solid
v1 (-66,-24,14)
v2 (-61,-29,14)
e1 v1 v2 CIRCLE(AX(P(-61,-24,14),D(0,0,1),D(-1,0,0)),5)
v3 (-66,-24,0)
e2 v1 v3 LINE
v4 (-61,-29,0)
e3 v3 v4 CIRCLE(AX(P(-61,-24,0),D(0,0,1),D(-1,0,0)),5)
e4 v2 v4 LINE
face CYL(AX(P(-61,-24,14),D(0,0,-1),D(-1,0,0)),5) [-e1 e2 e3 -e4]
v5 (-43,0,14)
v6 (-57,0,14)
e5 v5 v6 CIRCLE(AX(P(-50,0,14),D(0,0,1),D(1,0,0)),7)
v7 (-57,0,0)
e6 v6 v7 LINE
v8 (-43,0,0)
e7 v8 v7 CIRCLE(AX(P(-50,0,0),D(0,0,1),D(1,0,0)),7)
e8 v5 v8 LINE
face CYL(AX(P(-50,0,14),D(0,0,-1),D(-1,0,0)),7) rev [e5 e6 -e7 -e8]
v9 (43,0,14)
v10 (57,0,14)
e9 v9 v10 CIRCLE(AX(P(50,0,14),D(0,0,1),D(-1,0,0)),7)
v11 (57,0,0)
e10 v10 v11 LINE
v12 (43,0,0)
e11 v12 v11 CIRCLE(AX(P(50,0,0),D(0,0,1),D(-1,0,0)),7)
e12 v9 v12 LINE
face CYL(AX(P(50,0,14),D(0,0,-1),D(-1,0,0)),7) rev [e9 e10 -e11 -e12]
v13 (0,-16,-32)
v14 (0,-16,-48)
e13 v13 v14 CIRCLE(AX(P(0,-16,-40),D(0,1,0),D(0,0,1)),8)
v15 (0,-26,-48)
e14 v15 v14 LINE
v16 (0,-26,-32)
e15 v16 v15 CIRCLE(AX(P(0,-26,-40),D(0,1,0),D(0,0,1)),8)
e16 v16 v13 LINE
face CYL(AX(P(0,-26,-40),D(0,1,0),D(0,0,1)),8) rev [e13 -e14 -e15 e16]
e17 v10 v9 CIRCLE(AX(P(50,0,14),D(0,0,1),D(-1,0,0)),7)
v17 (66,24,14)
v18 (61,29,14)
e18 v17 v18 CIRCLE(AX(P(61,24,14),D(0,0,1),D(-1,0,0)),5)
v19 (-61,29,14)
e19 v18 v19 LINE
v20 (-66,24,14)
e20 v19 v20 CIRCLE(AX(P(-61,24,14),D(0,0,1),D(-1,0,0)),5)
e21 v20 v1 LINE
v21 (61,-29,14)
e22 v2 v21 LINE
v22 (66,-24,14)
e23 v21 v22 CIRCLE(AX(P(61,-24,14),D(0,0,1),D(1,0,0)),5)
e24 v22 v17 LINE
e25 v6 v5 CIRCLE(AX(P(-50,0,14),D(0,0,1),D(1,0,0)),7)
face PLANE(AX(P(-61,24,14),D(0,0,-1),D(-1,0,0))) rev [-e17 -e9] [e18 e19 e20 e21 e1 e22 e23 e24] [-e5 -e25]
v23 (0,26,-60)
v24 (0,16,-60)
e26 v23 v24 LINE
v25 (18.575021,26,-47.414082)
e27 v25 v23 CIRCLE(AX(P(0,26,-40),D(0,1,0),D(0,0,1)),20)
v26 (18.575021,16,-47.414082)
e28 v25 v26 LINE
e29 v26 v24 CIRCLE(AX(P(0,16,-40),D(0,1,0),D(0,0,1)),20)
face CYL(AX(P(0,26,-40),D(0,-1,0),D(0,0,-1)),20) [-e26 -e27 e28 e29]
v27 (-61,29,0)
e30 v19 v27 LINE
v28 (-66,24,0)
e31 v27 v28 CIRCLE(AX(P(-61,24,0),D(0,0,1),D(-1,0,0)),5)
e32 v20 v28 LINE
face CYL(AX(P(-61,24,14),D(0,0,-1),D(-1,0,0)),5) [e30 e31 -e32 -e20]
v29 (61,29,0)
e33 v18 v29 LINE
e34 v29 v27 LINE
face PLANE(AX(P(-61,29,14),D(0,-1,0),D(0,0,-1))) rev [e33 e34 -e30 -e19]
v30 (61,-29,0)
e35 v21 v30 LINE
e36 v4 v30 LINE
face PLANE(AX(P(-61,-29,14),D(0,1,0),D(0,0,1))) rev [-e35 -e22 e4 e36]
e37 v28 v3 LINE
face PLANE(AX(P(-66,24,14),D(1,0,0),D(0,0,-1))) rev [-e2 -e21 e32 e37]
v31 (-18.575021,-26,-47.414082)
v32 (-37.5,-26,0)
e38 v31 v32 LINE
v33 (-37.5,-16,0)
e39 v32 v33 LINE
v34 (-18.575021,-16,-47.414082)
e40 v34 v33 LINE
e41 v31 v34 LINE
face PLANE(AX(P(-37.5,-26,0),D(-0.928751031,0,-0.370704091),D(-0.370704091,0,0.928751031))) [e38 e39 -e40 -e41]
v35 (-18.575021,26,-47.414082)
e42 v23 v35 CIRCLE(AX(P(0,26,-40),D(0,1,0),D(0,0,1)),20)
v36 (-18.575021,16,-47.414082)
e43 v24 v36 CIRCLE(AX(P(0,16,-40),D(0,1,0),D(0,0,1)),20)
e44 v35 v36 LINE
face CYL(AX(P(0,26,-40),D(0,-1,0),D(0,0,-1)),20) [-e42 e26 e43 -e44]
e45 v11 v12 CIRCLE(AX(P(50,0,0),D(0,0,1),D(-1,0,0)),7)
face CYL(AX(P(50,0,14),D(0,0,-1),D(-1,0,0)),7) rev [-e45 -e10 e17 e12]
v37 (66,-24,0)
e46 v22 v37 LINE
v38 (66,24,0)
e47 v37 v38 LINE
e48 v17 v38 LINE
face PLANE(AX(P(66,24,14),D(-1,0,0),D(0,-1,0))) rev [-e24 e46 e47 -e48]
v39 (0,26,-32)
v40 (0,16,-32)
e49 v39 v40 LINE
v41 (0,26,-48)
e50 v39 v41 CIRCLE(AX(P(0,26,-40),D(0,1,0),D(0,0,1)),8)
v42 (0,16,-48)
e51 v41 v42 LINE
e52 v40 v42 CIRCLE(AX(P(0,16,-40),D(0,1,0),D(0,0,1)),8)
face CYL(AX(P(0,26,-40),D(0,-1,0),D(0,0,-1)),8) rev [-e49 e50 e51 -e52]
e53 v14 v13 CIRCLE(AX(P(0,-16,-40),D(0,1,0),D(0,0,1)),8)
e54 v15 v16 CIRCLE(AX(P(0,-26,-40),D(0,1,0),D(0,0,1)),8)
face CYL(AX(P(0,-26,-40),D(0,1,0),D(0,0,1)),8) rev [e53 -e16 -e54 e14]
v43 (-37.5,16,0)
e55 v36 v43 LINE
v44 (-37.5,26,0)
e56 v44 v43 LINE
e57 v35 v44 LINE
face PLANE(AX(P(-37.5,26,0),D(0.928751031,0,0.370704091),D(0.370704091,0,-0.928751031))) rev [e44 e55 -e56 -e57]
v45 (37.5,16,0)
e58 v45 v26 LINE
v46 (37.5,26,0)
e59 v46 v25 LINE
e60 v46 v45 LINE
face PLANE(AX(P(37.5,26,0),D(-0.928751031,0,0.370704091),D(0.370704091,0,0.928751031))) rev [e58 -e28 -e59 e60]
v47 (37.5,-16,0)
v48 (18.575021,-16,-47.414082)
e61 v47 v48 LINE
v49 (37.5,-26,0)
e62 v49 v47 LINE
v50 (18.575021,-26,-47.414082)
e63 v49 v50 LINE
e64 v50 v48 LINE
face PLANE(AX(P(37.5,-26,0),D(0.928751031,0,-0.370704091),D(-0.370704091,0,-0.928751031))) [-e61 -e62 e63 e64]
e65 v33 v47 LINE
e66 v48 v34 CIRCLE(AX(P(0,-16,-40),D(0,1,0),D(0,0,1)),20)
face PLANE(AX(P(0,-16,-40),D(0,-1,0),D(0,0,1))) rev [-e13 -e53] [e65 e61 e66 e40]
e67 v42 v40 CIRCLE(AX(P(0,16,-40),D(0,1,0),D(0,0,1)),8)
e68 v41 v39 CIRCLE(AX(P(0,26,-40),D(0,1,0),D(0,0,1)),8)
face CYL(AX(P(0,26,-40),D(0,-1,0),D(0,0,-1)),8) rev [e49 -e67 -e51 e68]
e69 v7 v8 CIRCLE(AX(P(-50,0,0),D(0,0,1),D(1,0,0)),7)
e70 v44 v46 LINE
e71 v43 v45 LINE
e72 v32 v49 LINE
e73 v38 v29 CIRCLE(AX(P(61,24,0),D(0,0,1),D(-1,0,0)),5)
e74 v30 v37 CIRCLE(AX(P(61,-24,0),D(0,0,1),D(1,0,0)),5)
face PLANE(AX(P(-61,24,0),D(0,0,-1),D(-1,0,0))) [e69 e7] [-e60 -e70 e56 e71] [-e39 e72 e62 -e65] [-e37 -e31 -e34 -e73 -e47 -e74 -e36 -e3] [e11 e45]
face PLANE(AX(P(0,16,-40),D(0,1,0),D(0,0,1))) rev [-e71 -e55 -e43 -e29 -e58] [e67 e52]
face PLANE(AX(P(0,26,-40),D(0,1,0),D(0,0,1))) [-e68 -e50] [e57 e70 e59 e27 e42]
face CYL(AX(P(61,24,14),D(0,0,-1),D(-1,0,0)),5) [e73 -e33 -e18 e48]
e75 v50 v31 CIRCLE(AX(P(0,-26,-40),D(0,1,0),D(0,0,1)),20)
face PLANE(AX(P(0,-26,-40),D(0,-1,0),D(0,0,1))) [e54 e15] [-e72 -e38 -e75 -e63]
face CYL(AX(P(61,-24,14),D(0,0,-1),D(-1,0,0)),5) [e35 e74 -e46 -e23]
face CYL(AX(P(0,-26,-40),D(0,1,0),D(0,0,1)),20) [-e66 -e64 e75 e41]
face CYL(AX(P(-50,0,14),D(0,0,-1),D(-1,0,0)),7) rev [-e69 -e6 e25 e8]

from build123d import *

# Parameters (mm, degrees)
BASE_PLATE_SKETCH_R = 7
BASE_PLATE_DEPTH    = 14
PIVOT_LUG_SKETCH_R  = 8
PIVOT_LUG_DEPTH     = 10


with BuildPart() as part:
    # Base Plate Sketch → Base Plate (new body)
    with BuildSketch(Plane.XY):
        with BuildLine():
            Line((-61, 29), (61, 29))
            ThreePointArc((61, 29), (64.535533906, 27.535533906), (66, 24))
            Line((66, 24), (66, -24))
            ThreePointArc((66, -24), (64.535533906, -27.535533906), (61, -29))
            Line((61, -29), (-61, -29))
            ThreePointArc((-61, -29), (-64.535533906, -27.535533906), (-66, -24))
            Line((-66, -24), (-66, 24))
            ThreePointArc((-66, 24), (-64.535533906, 27.535533906), (-61, 29))
        make_face()
        with Locations((-50, 0)):
            Circle(BASE_PLATE_SKETCH_R, mode=Mode.SUBTRACT)
        with Locations(Location((50, 0, 0), (0, 0, 180))):
            Circle(BASE_PLATE_SKETCH_R, mode=Mode.SUBTRACT)
    extrude(amount=BASE_PLATE_DEPTH)

    # Pivot Lug Sketch → Pivot Lug (add)
    with BuildSketch(Plane(origin=(0, 16, 0), x_dir=(1, 0, 0), z_dir=(0, 1, 0))):
        with BuildLine():
            Line((-37.5, 0), (37.5, 0))
            Line((37.5, 0), (18.575020612, 47.414081823))
            ThreePointArc((18.575020612, 47.414081823), (0, 60), (-18.575020612, 47.414081823))
            Line((-18.575020612, 47.414081823), (-37.5, 0))
        make_face()
        with Locations(Location((0, 40, 0), (0, 0, 270))):
            Circle(PIVOT_LUG_SKETCH_R, mode=Mode.SUBTRACT)
    pivot_lug = extrude(amount=PIVOT_LUG_DEPTH)

    # Pivot Lug Mirror: Pivot Lug across plane
    add(pivot_lug.mirror(Plane.ZX))


solid = part.part
